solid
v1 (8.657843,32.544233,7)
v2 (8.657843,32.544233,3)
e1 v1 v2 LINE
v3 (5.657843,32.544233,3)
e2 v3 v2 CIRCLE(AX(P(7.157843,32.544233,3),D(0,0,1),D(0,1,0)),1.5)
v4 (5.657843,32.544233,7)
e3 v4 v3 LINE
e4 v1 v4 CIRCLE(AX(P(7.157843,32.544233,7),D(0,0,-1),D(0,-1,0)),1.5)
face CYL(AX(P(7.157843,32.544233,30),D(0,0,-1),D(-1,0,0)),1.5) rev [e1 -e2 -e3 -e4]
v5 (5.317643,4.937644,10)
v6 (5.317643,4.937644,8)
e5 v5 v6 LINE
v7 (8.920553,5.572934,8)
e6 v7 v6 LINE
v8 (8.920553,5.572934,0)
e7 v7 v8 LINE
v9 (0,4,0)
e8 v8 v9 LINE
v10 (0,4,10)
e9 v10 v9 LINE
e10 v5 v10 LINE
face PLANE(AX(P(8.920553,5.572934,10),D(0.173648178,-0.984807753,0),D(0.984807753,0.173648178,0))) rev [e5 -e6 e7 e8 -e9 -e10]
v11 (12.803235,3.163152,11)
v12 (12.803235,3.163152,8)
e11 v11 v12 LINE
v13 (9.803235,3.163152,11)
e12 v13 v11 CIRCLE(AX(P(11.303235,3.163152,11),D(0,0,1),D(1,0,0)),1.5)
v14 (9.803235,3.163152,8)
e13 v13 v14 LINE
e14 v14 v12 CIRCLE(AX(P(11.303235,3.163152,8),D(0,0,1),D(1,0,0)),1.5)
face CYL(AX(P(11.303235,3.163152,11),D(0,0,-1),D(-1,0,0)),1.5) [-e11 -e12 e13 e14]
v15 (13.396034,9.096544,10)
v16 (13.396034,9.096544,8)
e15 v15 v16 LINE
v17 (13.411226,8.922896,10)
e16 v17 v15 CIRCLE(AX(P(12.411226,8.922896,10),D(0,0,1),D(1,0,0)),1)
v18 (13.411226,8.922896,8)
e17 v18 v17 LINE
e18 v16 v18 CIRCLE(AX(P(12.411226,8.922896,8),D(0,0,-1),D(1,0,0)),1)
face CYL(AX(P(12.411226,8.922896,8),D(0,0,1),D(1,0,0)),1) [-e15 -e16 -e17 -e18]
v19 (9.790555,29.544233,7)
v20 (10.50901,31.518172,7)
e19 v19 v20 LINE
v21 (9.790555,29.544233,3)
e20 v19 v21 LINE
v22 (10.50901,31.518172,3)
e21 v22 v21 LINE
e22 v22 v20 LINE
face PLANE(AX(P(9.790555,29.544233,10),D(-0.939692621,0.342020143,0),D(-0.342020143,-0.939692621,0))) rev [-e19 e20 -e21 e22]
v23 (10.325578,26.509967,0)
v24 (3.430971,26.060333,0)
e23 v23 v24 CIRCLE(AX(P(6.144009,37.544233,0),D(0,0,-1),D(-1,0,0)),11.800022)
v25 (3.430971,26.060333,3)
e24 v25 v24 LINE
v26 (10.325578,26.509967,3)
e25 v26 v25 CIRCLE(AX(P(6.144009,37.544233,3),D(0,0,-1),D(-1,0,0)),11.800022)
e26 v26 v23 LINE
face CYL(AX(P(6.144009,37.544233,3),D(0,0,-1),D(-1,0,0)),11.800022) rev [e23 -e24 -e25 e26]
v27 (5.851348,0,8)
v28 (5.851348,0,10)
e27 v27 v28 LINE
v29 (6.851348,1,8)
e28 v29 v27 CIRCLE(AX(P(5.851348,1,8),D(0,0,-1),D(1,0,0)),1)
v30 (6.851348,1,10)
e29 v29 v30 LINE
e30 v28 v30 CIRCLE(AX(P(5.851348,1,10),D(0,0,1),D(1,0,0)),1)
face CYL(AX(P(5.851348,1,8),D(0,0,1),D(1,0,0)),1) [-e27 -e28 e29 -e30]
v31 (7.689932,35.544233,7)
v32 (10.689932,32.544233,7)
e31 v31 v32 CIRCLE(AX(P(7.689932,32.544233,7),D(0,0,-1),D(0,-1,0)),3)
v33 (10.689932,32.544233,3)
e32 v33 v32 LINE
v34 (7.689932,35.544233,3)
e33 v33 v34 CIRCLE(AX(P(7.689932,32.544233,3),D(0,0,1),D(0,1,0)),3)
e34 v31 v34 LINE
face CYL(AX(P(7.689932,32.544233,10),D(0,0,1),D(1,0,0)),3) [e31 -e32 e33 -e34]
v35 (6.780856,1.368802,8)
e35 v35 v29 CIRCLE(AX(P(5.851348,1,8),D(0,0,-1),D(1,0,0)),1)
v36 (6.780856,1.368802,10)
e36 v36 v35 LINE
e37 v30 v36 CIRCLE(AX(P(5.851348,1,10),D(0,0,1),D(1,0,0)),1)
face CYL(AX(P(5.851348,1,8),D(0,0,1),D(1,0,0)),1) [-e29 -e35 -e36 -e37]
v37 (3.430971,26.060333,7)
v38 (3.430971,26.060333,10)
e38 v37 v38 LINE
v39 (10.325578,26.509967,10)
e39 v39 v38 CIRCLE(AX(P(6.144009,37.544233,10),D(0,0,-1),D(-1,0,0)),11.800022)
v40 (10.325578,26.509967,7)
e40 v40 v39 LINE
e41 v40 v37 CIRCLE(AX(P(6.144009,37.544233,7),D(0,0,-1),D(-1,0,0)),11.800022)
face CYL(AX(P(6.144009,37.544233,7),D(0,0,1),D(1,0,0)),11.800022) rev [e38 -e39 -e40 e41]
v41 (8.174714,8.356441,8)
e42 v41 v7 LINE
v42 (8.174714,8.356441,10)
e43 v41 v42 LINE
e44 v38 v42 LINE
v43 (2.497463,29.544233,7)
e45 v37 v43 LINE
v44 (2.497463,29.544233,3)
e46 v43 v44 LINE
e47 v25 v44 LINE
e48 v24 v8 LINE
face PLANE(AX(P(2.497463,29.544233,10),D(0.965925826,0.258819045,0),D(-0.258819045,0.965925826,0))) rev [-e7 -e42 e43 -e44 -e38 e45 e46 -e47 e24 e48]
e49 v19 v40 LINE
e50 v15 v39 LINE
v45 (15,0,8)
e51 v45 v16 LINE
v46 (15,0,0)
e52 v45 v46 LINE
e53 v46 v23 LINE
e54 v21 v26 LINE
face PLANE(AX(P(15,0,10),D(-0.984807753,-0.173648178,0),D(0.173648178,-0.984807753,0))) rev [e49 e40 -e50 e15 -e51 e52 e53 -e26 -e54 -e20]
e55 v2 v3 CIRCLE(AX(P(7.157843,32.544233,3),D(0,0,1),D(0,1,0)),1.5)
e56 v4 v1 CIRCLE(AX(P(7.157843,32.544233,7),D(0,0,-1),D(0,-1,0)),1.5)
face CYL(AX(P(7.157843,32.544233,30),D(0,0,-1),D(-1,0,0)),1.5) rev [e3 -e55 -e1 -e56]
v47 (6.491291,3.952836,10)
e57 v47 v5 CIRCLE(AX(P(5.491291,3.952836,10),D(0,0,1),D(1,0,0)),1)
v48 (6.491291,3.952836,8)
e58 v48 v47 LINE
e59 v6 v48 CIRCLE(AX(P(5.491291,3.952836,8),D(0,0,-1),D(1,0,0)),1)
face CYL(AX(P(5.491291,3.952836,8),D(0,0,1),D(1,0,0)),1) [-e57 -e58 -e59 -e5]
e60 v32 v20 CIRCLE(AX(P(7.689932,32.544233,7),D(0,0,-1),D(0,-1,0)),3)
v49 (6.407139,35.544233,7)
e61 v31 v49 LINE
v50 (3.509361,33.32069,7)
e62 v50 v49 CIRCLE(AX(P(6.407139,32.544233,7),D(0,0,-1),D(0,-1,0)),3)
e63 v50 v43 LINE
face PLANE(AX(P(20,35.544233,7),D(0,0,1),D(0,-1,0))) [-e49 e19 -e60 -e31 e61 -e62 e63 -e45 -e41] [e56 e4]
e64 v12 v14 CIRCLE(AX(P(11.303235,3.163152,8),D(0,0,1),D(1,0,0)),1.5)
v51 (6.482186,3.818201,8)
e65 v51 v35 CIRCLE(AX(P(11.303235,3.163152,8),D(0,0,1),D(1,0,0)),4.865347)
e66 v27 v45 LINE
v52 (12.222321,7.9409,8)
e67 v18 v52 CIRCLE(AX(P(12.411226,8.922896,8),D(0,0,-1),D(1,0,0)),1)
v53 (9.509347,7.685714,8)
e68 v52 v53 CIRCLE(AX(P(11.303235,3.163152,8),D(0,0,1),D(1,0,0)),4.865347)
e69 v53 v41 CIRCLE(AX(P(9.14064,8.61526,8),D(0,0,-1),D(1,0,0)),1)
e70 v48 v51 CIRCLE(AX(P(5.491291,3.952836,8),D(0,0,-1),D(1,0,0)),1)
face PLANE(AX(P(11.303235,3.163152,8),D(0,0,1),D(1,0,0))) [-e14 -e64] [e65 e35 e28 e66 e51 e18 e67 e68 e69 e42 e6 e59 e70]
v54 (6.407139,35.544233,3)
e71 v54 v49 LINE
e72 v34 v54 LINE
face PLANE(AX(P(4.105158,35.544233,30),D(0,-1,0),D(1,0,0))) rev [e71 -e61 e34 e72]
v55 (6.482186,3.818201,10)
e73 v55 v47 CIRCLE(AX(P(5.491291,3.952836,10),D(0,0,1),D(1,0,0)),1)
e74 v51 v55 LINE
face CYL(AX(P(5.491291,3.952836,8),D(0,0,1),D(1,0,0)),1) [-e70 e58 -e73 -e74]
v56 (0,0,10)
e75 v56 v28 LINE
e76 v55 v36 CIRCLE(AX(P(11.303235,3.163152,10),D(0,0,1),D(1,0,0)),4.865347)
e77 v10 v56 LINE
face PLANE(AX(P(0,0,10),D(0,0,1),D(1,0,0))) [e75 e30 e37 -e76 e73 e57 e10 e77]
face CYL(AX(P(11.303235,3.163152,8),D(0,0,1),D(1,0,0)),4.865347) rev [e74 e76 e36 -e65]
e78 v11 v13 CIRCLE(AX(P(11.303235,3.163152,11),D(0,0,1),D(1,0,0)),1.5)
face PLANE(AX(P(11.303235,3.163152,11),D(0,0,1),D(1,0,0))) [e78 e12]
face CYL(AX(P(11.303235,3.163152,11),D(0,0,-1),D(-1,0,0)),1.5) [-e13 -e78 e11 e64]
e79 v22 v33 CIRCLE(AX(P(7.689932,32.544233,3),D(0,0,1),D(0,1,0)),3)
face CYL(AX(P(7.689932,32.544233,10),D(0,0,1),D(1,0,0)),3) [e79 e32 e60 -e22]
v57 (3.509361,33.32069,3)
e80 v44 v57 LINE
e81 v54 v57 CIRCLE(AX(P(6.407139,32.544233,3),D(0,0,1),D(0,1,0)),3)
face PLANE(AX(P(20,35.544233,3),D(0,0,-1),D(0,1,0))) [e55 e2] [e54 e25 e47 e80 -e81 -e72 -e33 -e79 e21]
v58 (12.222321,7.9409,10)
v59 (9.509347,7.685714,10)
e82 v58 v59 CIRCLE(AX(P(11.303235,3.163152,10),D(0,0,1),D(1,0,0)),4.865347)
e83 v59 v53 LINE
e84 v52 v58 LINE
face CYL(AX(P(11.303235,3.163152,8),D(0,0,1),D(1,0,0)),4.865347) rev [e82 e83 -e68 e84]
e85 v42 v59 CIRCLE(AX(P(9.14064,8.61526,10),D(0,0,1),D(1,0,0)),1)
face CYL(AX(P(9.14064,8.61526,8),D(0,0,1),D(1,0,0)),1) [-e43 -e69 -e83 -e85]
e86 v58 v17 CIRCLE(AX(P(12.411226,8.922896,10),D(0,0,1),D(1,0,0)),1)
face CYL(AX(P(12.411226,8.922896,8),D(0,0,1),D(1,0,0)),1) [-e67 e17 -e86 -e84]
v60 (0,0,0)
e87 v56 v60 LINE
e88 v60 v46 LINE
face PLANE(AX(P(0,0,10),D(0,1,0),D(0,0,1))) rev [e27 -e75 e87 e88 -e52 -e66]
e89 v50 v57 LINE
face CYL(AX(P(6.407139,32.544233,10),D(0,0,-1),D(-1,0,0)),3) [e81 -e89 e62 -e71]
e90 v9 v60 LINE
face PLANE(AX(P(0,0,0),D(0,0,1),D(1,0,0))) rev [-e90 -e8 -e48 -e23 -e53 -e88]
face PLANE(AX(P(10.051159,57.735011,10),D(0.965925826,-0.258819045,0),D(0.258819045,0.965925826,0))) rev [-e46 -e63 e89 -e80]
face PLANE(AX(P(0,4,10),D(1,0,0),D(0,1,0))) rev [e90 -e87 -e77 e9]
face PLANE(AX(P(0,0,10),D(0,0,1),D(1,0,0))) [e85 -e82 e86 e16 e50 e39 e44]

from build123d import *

# Parameters (mm, degrees)
BOSS_EXTRUDE1_DEPTH = 10
SKETCH2_W           = 14
SKETCH2_H           = 30
BOSS_EXTRUDE2_DEPTH = 30
BOSS_EXTRUDE4_DEPTH = 5
SKETCH5_W           = 6
SKETCH5_H           = 7
BOSS_EXTRUDE5_DEPTH = 6
SKETCH6_W           = 15
SKETCH6_H           = 15
BOSS_EXTRUDE6_DEPTH = 14
SKETCH7_R           = 1
CUT_EXTRUDE1_DEPTH  = 2
FILLET1_R           = 1
SKETCH8_R           = 1.5
SKETCH8_W           = 21.297654542
SKETCH8_H           = 29.54423259
CUT_EXTRUDE2_DEPTH  = 10
SKETCH9_W           = 4
SKETCH9_H           = 12
CUT_EXTRUDE3_DEPTH  = 7.5
SKETCH11_R          = 1.5
SKETCH11_W          = 46.682021109
SKETCH11_H          = 78.101327177
CUT_EXTRUDE6_DEPTH  = 50
SKETCH12_W          = 25.193851166
SKETCH12_H          = 16.960566472
CUT_EXTRUDE7_DEPTH  = 20
FILLET2_R           = 3
SKETCH13_W          = 3
SKETCH13_H          = 6
CUT_EXTRUDE8_DEPTH  = 20
SKETCH14_R          = 11.800022464
CUT_EXTRUDE9_DEPTH  = 3
SKETCH15_R          = 1.5
BOSS_EXTRUDE7_DEPTH = 1
SKETCH16_R          = 4.865347009
SKETCH16_R_2        = 1.5
CUT_EXTRUDE10_DEPTH = 2
FILLET5_R           = 1


with BuildPart() as part:
    # Sketch1 → Boss-Extrude1 (new body)
    with BuildSketch(Plane.XY):
        Polygon((0, 0), (15, 0), (9.79055467, 29.54423259), (20.05115897, 57.735011214), (10.05115897, 57.735011214), (2.497462604, 29.54423259), (8.920552671, 5.572934119), (0, 4), align=None)
    boss_extrude1 = extrude(amount=BOSS_EXTRUDE1_DEPTH)

    # Sketch2 → Boss-Extrude2 (add)
    with BuildSketch(Plane.XY.offset(10)):
        with Locations((15.05115897, 72.735011214)):
            Rectangle(SKETCH2_W, SKETCH2_H)
    extrude(amount=-BOSS_EXTRUDE2_DEPTH)

    # Sketch4 → Boss-Extrude4 (add)
    with BuildSketch(Plane.XY.offset(10)):
        Polygon((15.05115897, 84.235011214), (30.372047832, 71.37925902), (30.372047832, 56.37925902), (27.30787006, 56.37925902), (27.30787006, 68.950409459), (15.05115897, 79.235011214), align=None)
    boss_extrude4 = extrude(amount=BOSS_EXTRUDE4_DEPTH)

    # Mirror1: Boss-Extrude1, Boss-Extrude4 across plane
    add(boss_extrude1.mirror(Plane.XY.offset(-5)))
    add(boss_extrude4.mirror(Plane.XY.offset(-5)))

    # Sketch5 → Boss-Extrude5 (add)
    with BuildSketch(Plane(origin=(0, 87.735011214, 0), x_dir=(1, 0, 0), z_dir=(0, 1, 0))):
        with Locations((15.05115897, 5)):
            Rectangle(SKETCH5_W, SKETCH5_H)
    extrude(amount=BOSS_EXTRUDE5_DEPTH)

    # Sketch6 → Boss-Extrude6 (add)
    with BuildSketch(Plane(origin=(0, 93.735011214, 0), x_dir=(1, 0, 0), z_dir=(0, 1, 0))):
        with Locations((15.05115897, 5)):
            Rectangle(SKETCH6_W, SKETCH6_H)
    extrude(amount=BOSS_EXTRUDE6_DEPTH)

    # Sketch7 → Cut-Extrude1 (cut)
    with BuildSketch(Plane.ZY.offset(-7.55115897)):
        with Locations((-8.96, 103.735011214)):
            Circle(SKETCH7_R)
        with Locations(Location((-1.04, 103.735011214, 0), (0, 0, 180))):
            Circle(SKETCH7_R)
    extrude(amount=-CUT_EXTRUDE1_DEPTH, mode=Mode.SUBTRACT)

    # Fillet1
    fillet1_edges = [part.edges().sort_by_distance(p)[0] for p in [
        (18.55115897, 81.298162505, 10),
        (15.05115897, 81.735011214, 10),
        (15.05115897, 84.235011214, 12.5),
        (18.55115897, 76.298162505, 10),
        (15.05115897, 79.235011214, 12.5),
        (18.55115897, 81.298162505, -20),
        (18.55115897, 76.298162505, -20),
        (15.05115897, 81.735011214, -20),
        (15.05115897, 79.235011214, -22.5),
        (15.05115897, 84.235011214, -22.5),
    ]]
    fillet(fillet1_edges, radius=FILLET1_R)

    # Sketch8 → Cut-Extrude2 (cut)
    with BuildSketch(Plane(origin=(0, 0, -20), x_dir=(-1, 0, 0), z_dir=(0, 0, -1))):
        with Locations((-7.157843169, 32.54423259)):
            Circle(SKETCH8_R)
        with Locations((-4.351172729, 14.772116295)):
            Rectangle(SKETCH8_W, SKETCH8_H)
    extrude(amount=-CUT_EXTRUDE2_DEPTH, mode=Mode.SUBTRACT)

    # Sketch9 → Cut-Extrude3 (cut, symmetric)
    with BuildSketch(Plane.ZY.offset(-8.05115897)):
        with Locations((-15, 30.54423259)):
            Rectangle(SKETCH9_W, SKETCH9_H)
    extrude(amount=CUT_EXTRUDE3_DEPTH, both=True, mode=Mode.SUBTRACT)

    # Sketch11 → Cut-Extrude6 (cut, symmetric)
    with BuildSketch(Plane(origin=(0, 0, -20), x_dir=(-1, 0, 0), z_dir=(0, 0, -1))):
        with Locations(Location((-7.157843169, 32.54423259, 0), (0, 0, 180))):
            Circle(SKETCH11_R)
        with Locations((-27.446168312, 74.594896179)):
            Rectangle(SKETCH11_W, SKETCH11_H)
    extrude(amount=CUT_EXTRUDE6_DEPTH, both=True, mode=Mode.SUBTRACT)


with BuildPart() as cut_extrude6_piece_1:
    # of the separate pieces the step leaves, piece 1, a body of its own (cut_extrude6_pieces)
    add(part.part.solids().sort_by_distance((4.105157758, 35.54423259, 10))[0])

    # Fillet2
    fillet2_edges = [cut_extrude6_piece_1.edges().sort_by_distance(p)[0] for p in [
        (11.974376076, 35.54423259, 5),
        (4.105157758, 35.54423259, 5),
    ]]
    fillet(fillet2_edges, radius=FILLET2_R)

    # Sketch13 → Cut-Extrude8 (cut)
    with BuildSketch(Plane(origin=(0, 0, 0), x_dir=(0, 0, -1), z_dir=(1, 0, 0))):
        with Locations((-8.5, 32.54423259)):
            Rectangle(SKETCH13_W, SKETCH13_H)
        with Locations((-1.5, 32.54423259)):
            Rectangle(SKETCH13_W, SKETCH13_H)
    extrude(amount=CUT_EXTRUDE8_DEPTH, mode=Mode.SUBTRACT)

    # Sketch14 → Cut-Extrude9 (cut)
    with BuildSketch(Plane(origin=(0, 0, 0), x_dir=(-1, 0, 0), z_dir=(0, 0, -1))):
        with Locations((-6.144008637, 37.54423259)):
            Circle(SKETCH14_R)
    cut_extrude9 = extrude(amount=-CUT_EXTRUDE9_DEPTH, mode=Mode.SUBTRACT)

    # Mirror2: Cut-Extrude9 across plane
    add(cut_extrude9.mirror(Plane(origin=(0, 0, 5), x_dir=(1, 0, 0), z_dir=(0, 0, -1))), mode=Mode.SUBTRACT)

    # Sketch15 → Boss-Extrude7 (add)
    with BuildSketch(Plane.XY.offset(10)):
        with Locations((11.303234902, 3.163151803)):
            Circle(SKETCH15_R)
    extrude(amount=BOSS_EXTRUDE7_DEPTH)

    # Sketch16 → Cut-Extrude10 (cut)
    with BuildSketch(Plane.XY.offset(10)):
        with Locations((11.303234902, 3.163151803)):
            Circle(SKETCH16_R)
        with Locations((11.303234902, 3.163151803)):
            Circle(SKETCH16_R_2, mode=Mode.SUBTRACT)
    extrude(amount=-CUT_EXTRUDE10_DEPTH, mode=Mode.SUBTRACT)

    # Fillet5
    fillet5_edges = [cut_extrude6_piece_1.edges().sort_by_distance(p)[0] for p in [
        (6.891812395, 5.215212471, 9),
        (13.695196152, 7.399910339, 9),
        (8.500606317, 7.140195245, 9),
        (7.606469803, 0, 9),
    ]]
    fillet(fillet5_edges, radius=FILLET5_R)


with BuildPart() as cut_extrude6_piece_2:
    # of the separate pieces the step leaves, piece 2, a body of its own (cut_extrude6_pieces)
    add(part.part.solids().sort_by_distance((4.105157758, 35.54423259, -20))[0])


with BuildPart() as cut_extrude6_piece_3:
    # of the separate pieces the step leaves, piece 3, a body of its own (cut_extrude6_pieces)
    add(part.part.solids().sort_by_distance((4.105157758, 35.54423259, -10))[0])


with BuildPart() as cut_extrude7_tool:
    # Sketch12 → Cut-Extrude7 (new body)
    with BuildSketch(Plane(origin=(0, 0, -20), x_dir=(-1, 0, 0), z_dir=(0, 0, -1))):
        with Locations((-9.102890418, 33.861350945)):
            Rectangle(SKETCH12_W, SKETCH12_H)
    extrude(amount=-CUT_EXTRUDE7_DEPTH)


with BuildPart() as cut_extrude6_piece_2_1:
    add(cut_extrude6_piece_2.part)

    # Cut-Extrude7: cut by cut_extrude7_tool
    add(cut_extrude7_tool.part, mode=Mode.SUBTRACT)


with BuildPart() as cut_extrude6_piece_3_1:
    add(cut_extrude6_piece_3.part)

    # Cut-Extrude7: cut by cut_extrude7_tool
    add(cut_extrude7_tool.part, mode=Mode.SUBTRACT)


solid = cut_extrude6_piece_1.part
